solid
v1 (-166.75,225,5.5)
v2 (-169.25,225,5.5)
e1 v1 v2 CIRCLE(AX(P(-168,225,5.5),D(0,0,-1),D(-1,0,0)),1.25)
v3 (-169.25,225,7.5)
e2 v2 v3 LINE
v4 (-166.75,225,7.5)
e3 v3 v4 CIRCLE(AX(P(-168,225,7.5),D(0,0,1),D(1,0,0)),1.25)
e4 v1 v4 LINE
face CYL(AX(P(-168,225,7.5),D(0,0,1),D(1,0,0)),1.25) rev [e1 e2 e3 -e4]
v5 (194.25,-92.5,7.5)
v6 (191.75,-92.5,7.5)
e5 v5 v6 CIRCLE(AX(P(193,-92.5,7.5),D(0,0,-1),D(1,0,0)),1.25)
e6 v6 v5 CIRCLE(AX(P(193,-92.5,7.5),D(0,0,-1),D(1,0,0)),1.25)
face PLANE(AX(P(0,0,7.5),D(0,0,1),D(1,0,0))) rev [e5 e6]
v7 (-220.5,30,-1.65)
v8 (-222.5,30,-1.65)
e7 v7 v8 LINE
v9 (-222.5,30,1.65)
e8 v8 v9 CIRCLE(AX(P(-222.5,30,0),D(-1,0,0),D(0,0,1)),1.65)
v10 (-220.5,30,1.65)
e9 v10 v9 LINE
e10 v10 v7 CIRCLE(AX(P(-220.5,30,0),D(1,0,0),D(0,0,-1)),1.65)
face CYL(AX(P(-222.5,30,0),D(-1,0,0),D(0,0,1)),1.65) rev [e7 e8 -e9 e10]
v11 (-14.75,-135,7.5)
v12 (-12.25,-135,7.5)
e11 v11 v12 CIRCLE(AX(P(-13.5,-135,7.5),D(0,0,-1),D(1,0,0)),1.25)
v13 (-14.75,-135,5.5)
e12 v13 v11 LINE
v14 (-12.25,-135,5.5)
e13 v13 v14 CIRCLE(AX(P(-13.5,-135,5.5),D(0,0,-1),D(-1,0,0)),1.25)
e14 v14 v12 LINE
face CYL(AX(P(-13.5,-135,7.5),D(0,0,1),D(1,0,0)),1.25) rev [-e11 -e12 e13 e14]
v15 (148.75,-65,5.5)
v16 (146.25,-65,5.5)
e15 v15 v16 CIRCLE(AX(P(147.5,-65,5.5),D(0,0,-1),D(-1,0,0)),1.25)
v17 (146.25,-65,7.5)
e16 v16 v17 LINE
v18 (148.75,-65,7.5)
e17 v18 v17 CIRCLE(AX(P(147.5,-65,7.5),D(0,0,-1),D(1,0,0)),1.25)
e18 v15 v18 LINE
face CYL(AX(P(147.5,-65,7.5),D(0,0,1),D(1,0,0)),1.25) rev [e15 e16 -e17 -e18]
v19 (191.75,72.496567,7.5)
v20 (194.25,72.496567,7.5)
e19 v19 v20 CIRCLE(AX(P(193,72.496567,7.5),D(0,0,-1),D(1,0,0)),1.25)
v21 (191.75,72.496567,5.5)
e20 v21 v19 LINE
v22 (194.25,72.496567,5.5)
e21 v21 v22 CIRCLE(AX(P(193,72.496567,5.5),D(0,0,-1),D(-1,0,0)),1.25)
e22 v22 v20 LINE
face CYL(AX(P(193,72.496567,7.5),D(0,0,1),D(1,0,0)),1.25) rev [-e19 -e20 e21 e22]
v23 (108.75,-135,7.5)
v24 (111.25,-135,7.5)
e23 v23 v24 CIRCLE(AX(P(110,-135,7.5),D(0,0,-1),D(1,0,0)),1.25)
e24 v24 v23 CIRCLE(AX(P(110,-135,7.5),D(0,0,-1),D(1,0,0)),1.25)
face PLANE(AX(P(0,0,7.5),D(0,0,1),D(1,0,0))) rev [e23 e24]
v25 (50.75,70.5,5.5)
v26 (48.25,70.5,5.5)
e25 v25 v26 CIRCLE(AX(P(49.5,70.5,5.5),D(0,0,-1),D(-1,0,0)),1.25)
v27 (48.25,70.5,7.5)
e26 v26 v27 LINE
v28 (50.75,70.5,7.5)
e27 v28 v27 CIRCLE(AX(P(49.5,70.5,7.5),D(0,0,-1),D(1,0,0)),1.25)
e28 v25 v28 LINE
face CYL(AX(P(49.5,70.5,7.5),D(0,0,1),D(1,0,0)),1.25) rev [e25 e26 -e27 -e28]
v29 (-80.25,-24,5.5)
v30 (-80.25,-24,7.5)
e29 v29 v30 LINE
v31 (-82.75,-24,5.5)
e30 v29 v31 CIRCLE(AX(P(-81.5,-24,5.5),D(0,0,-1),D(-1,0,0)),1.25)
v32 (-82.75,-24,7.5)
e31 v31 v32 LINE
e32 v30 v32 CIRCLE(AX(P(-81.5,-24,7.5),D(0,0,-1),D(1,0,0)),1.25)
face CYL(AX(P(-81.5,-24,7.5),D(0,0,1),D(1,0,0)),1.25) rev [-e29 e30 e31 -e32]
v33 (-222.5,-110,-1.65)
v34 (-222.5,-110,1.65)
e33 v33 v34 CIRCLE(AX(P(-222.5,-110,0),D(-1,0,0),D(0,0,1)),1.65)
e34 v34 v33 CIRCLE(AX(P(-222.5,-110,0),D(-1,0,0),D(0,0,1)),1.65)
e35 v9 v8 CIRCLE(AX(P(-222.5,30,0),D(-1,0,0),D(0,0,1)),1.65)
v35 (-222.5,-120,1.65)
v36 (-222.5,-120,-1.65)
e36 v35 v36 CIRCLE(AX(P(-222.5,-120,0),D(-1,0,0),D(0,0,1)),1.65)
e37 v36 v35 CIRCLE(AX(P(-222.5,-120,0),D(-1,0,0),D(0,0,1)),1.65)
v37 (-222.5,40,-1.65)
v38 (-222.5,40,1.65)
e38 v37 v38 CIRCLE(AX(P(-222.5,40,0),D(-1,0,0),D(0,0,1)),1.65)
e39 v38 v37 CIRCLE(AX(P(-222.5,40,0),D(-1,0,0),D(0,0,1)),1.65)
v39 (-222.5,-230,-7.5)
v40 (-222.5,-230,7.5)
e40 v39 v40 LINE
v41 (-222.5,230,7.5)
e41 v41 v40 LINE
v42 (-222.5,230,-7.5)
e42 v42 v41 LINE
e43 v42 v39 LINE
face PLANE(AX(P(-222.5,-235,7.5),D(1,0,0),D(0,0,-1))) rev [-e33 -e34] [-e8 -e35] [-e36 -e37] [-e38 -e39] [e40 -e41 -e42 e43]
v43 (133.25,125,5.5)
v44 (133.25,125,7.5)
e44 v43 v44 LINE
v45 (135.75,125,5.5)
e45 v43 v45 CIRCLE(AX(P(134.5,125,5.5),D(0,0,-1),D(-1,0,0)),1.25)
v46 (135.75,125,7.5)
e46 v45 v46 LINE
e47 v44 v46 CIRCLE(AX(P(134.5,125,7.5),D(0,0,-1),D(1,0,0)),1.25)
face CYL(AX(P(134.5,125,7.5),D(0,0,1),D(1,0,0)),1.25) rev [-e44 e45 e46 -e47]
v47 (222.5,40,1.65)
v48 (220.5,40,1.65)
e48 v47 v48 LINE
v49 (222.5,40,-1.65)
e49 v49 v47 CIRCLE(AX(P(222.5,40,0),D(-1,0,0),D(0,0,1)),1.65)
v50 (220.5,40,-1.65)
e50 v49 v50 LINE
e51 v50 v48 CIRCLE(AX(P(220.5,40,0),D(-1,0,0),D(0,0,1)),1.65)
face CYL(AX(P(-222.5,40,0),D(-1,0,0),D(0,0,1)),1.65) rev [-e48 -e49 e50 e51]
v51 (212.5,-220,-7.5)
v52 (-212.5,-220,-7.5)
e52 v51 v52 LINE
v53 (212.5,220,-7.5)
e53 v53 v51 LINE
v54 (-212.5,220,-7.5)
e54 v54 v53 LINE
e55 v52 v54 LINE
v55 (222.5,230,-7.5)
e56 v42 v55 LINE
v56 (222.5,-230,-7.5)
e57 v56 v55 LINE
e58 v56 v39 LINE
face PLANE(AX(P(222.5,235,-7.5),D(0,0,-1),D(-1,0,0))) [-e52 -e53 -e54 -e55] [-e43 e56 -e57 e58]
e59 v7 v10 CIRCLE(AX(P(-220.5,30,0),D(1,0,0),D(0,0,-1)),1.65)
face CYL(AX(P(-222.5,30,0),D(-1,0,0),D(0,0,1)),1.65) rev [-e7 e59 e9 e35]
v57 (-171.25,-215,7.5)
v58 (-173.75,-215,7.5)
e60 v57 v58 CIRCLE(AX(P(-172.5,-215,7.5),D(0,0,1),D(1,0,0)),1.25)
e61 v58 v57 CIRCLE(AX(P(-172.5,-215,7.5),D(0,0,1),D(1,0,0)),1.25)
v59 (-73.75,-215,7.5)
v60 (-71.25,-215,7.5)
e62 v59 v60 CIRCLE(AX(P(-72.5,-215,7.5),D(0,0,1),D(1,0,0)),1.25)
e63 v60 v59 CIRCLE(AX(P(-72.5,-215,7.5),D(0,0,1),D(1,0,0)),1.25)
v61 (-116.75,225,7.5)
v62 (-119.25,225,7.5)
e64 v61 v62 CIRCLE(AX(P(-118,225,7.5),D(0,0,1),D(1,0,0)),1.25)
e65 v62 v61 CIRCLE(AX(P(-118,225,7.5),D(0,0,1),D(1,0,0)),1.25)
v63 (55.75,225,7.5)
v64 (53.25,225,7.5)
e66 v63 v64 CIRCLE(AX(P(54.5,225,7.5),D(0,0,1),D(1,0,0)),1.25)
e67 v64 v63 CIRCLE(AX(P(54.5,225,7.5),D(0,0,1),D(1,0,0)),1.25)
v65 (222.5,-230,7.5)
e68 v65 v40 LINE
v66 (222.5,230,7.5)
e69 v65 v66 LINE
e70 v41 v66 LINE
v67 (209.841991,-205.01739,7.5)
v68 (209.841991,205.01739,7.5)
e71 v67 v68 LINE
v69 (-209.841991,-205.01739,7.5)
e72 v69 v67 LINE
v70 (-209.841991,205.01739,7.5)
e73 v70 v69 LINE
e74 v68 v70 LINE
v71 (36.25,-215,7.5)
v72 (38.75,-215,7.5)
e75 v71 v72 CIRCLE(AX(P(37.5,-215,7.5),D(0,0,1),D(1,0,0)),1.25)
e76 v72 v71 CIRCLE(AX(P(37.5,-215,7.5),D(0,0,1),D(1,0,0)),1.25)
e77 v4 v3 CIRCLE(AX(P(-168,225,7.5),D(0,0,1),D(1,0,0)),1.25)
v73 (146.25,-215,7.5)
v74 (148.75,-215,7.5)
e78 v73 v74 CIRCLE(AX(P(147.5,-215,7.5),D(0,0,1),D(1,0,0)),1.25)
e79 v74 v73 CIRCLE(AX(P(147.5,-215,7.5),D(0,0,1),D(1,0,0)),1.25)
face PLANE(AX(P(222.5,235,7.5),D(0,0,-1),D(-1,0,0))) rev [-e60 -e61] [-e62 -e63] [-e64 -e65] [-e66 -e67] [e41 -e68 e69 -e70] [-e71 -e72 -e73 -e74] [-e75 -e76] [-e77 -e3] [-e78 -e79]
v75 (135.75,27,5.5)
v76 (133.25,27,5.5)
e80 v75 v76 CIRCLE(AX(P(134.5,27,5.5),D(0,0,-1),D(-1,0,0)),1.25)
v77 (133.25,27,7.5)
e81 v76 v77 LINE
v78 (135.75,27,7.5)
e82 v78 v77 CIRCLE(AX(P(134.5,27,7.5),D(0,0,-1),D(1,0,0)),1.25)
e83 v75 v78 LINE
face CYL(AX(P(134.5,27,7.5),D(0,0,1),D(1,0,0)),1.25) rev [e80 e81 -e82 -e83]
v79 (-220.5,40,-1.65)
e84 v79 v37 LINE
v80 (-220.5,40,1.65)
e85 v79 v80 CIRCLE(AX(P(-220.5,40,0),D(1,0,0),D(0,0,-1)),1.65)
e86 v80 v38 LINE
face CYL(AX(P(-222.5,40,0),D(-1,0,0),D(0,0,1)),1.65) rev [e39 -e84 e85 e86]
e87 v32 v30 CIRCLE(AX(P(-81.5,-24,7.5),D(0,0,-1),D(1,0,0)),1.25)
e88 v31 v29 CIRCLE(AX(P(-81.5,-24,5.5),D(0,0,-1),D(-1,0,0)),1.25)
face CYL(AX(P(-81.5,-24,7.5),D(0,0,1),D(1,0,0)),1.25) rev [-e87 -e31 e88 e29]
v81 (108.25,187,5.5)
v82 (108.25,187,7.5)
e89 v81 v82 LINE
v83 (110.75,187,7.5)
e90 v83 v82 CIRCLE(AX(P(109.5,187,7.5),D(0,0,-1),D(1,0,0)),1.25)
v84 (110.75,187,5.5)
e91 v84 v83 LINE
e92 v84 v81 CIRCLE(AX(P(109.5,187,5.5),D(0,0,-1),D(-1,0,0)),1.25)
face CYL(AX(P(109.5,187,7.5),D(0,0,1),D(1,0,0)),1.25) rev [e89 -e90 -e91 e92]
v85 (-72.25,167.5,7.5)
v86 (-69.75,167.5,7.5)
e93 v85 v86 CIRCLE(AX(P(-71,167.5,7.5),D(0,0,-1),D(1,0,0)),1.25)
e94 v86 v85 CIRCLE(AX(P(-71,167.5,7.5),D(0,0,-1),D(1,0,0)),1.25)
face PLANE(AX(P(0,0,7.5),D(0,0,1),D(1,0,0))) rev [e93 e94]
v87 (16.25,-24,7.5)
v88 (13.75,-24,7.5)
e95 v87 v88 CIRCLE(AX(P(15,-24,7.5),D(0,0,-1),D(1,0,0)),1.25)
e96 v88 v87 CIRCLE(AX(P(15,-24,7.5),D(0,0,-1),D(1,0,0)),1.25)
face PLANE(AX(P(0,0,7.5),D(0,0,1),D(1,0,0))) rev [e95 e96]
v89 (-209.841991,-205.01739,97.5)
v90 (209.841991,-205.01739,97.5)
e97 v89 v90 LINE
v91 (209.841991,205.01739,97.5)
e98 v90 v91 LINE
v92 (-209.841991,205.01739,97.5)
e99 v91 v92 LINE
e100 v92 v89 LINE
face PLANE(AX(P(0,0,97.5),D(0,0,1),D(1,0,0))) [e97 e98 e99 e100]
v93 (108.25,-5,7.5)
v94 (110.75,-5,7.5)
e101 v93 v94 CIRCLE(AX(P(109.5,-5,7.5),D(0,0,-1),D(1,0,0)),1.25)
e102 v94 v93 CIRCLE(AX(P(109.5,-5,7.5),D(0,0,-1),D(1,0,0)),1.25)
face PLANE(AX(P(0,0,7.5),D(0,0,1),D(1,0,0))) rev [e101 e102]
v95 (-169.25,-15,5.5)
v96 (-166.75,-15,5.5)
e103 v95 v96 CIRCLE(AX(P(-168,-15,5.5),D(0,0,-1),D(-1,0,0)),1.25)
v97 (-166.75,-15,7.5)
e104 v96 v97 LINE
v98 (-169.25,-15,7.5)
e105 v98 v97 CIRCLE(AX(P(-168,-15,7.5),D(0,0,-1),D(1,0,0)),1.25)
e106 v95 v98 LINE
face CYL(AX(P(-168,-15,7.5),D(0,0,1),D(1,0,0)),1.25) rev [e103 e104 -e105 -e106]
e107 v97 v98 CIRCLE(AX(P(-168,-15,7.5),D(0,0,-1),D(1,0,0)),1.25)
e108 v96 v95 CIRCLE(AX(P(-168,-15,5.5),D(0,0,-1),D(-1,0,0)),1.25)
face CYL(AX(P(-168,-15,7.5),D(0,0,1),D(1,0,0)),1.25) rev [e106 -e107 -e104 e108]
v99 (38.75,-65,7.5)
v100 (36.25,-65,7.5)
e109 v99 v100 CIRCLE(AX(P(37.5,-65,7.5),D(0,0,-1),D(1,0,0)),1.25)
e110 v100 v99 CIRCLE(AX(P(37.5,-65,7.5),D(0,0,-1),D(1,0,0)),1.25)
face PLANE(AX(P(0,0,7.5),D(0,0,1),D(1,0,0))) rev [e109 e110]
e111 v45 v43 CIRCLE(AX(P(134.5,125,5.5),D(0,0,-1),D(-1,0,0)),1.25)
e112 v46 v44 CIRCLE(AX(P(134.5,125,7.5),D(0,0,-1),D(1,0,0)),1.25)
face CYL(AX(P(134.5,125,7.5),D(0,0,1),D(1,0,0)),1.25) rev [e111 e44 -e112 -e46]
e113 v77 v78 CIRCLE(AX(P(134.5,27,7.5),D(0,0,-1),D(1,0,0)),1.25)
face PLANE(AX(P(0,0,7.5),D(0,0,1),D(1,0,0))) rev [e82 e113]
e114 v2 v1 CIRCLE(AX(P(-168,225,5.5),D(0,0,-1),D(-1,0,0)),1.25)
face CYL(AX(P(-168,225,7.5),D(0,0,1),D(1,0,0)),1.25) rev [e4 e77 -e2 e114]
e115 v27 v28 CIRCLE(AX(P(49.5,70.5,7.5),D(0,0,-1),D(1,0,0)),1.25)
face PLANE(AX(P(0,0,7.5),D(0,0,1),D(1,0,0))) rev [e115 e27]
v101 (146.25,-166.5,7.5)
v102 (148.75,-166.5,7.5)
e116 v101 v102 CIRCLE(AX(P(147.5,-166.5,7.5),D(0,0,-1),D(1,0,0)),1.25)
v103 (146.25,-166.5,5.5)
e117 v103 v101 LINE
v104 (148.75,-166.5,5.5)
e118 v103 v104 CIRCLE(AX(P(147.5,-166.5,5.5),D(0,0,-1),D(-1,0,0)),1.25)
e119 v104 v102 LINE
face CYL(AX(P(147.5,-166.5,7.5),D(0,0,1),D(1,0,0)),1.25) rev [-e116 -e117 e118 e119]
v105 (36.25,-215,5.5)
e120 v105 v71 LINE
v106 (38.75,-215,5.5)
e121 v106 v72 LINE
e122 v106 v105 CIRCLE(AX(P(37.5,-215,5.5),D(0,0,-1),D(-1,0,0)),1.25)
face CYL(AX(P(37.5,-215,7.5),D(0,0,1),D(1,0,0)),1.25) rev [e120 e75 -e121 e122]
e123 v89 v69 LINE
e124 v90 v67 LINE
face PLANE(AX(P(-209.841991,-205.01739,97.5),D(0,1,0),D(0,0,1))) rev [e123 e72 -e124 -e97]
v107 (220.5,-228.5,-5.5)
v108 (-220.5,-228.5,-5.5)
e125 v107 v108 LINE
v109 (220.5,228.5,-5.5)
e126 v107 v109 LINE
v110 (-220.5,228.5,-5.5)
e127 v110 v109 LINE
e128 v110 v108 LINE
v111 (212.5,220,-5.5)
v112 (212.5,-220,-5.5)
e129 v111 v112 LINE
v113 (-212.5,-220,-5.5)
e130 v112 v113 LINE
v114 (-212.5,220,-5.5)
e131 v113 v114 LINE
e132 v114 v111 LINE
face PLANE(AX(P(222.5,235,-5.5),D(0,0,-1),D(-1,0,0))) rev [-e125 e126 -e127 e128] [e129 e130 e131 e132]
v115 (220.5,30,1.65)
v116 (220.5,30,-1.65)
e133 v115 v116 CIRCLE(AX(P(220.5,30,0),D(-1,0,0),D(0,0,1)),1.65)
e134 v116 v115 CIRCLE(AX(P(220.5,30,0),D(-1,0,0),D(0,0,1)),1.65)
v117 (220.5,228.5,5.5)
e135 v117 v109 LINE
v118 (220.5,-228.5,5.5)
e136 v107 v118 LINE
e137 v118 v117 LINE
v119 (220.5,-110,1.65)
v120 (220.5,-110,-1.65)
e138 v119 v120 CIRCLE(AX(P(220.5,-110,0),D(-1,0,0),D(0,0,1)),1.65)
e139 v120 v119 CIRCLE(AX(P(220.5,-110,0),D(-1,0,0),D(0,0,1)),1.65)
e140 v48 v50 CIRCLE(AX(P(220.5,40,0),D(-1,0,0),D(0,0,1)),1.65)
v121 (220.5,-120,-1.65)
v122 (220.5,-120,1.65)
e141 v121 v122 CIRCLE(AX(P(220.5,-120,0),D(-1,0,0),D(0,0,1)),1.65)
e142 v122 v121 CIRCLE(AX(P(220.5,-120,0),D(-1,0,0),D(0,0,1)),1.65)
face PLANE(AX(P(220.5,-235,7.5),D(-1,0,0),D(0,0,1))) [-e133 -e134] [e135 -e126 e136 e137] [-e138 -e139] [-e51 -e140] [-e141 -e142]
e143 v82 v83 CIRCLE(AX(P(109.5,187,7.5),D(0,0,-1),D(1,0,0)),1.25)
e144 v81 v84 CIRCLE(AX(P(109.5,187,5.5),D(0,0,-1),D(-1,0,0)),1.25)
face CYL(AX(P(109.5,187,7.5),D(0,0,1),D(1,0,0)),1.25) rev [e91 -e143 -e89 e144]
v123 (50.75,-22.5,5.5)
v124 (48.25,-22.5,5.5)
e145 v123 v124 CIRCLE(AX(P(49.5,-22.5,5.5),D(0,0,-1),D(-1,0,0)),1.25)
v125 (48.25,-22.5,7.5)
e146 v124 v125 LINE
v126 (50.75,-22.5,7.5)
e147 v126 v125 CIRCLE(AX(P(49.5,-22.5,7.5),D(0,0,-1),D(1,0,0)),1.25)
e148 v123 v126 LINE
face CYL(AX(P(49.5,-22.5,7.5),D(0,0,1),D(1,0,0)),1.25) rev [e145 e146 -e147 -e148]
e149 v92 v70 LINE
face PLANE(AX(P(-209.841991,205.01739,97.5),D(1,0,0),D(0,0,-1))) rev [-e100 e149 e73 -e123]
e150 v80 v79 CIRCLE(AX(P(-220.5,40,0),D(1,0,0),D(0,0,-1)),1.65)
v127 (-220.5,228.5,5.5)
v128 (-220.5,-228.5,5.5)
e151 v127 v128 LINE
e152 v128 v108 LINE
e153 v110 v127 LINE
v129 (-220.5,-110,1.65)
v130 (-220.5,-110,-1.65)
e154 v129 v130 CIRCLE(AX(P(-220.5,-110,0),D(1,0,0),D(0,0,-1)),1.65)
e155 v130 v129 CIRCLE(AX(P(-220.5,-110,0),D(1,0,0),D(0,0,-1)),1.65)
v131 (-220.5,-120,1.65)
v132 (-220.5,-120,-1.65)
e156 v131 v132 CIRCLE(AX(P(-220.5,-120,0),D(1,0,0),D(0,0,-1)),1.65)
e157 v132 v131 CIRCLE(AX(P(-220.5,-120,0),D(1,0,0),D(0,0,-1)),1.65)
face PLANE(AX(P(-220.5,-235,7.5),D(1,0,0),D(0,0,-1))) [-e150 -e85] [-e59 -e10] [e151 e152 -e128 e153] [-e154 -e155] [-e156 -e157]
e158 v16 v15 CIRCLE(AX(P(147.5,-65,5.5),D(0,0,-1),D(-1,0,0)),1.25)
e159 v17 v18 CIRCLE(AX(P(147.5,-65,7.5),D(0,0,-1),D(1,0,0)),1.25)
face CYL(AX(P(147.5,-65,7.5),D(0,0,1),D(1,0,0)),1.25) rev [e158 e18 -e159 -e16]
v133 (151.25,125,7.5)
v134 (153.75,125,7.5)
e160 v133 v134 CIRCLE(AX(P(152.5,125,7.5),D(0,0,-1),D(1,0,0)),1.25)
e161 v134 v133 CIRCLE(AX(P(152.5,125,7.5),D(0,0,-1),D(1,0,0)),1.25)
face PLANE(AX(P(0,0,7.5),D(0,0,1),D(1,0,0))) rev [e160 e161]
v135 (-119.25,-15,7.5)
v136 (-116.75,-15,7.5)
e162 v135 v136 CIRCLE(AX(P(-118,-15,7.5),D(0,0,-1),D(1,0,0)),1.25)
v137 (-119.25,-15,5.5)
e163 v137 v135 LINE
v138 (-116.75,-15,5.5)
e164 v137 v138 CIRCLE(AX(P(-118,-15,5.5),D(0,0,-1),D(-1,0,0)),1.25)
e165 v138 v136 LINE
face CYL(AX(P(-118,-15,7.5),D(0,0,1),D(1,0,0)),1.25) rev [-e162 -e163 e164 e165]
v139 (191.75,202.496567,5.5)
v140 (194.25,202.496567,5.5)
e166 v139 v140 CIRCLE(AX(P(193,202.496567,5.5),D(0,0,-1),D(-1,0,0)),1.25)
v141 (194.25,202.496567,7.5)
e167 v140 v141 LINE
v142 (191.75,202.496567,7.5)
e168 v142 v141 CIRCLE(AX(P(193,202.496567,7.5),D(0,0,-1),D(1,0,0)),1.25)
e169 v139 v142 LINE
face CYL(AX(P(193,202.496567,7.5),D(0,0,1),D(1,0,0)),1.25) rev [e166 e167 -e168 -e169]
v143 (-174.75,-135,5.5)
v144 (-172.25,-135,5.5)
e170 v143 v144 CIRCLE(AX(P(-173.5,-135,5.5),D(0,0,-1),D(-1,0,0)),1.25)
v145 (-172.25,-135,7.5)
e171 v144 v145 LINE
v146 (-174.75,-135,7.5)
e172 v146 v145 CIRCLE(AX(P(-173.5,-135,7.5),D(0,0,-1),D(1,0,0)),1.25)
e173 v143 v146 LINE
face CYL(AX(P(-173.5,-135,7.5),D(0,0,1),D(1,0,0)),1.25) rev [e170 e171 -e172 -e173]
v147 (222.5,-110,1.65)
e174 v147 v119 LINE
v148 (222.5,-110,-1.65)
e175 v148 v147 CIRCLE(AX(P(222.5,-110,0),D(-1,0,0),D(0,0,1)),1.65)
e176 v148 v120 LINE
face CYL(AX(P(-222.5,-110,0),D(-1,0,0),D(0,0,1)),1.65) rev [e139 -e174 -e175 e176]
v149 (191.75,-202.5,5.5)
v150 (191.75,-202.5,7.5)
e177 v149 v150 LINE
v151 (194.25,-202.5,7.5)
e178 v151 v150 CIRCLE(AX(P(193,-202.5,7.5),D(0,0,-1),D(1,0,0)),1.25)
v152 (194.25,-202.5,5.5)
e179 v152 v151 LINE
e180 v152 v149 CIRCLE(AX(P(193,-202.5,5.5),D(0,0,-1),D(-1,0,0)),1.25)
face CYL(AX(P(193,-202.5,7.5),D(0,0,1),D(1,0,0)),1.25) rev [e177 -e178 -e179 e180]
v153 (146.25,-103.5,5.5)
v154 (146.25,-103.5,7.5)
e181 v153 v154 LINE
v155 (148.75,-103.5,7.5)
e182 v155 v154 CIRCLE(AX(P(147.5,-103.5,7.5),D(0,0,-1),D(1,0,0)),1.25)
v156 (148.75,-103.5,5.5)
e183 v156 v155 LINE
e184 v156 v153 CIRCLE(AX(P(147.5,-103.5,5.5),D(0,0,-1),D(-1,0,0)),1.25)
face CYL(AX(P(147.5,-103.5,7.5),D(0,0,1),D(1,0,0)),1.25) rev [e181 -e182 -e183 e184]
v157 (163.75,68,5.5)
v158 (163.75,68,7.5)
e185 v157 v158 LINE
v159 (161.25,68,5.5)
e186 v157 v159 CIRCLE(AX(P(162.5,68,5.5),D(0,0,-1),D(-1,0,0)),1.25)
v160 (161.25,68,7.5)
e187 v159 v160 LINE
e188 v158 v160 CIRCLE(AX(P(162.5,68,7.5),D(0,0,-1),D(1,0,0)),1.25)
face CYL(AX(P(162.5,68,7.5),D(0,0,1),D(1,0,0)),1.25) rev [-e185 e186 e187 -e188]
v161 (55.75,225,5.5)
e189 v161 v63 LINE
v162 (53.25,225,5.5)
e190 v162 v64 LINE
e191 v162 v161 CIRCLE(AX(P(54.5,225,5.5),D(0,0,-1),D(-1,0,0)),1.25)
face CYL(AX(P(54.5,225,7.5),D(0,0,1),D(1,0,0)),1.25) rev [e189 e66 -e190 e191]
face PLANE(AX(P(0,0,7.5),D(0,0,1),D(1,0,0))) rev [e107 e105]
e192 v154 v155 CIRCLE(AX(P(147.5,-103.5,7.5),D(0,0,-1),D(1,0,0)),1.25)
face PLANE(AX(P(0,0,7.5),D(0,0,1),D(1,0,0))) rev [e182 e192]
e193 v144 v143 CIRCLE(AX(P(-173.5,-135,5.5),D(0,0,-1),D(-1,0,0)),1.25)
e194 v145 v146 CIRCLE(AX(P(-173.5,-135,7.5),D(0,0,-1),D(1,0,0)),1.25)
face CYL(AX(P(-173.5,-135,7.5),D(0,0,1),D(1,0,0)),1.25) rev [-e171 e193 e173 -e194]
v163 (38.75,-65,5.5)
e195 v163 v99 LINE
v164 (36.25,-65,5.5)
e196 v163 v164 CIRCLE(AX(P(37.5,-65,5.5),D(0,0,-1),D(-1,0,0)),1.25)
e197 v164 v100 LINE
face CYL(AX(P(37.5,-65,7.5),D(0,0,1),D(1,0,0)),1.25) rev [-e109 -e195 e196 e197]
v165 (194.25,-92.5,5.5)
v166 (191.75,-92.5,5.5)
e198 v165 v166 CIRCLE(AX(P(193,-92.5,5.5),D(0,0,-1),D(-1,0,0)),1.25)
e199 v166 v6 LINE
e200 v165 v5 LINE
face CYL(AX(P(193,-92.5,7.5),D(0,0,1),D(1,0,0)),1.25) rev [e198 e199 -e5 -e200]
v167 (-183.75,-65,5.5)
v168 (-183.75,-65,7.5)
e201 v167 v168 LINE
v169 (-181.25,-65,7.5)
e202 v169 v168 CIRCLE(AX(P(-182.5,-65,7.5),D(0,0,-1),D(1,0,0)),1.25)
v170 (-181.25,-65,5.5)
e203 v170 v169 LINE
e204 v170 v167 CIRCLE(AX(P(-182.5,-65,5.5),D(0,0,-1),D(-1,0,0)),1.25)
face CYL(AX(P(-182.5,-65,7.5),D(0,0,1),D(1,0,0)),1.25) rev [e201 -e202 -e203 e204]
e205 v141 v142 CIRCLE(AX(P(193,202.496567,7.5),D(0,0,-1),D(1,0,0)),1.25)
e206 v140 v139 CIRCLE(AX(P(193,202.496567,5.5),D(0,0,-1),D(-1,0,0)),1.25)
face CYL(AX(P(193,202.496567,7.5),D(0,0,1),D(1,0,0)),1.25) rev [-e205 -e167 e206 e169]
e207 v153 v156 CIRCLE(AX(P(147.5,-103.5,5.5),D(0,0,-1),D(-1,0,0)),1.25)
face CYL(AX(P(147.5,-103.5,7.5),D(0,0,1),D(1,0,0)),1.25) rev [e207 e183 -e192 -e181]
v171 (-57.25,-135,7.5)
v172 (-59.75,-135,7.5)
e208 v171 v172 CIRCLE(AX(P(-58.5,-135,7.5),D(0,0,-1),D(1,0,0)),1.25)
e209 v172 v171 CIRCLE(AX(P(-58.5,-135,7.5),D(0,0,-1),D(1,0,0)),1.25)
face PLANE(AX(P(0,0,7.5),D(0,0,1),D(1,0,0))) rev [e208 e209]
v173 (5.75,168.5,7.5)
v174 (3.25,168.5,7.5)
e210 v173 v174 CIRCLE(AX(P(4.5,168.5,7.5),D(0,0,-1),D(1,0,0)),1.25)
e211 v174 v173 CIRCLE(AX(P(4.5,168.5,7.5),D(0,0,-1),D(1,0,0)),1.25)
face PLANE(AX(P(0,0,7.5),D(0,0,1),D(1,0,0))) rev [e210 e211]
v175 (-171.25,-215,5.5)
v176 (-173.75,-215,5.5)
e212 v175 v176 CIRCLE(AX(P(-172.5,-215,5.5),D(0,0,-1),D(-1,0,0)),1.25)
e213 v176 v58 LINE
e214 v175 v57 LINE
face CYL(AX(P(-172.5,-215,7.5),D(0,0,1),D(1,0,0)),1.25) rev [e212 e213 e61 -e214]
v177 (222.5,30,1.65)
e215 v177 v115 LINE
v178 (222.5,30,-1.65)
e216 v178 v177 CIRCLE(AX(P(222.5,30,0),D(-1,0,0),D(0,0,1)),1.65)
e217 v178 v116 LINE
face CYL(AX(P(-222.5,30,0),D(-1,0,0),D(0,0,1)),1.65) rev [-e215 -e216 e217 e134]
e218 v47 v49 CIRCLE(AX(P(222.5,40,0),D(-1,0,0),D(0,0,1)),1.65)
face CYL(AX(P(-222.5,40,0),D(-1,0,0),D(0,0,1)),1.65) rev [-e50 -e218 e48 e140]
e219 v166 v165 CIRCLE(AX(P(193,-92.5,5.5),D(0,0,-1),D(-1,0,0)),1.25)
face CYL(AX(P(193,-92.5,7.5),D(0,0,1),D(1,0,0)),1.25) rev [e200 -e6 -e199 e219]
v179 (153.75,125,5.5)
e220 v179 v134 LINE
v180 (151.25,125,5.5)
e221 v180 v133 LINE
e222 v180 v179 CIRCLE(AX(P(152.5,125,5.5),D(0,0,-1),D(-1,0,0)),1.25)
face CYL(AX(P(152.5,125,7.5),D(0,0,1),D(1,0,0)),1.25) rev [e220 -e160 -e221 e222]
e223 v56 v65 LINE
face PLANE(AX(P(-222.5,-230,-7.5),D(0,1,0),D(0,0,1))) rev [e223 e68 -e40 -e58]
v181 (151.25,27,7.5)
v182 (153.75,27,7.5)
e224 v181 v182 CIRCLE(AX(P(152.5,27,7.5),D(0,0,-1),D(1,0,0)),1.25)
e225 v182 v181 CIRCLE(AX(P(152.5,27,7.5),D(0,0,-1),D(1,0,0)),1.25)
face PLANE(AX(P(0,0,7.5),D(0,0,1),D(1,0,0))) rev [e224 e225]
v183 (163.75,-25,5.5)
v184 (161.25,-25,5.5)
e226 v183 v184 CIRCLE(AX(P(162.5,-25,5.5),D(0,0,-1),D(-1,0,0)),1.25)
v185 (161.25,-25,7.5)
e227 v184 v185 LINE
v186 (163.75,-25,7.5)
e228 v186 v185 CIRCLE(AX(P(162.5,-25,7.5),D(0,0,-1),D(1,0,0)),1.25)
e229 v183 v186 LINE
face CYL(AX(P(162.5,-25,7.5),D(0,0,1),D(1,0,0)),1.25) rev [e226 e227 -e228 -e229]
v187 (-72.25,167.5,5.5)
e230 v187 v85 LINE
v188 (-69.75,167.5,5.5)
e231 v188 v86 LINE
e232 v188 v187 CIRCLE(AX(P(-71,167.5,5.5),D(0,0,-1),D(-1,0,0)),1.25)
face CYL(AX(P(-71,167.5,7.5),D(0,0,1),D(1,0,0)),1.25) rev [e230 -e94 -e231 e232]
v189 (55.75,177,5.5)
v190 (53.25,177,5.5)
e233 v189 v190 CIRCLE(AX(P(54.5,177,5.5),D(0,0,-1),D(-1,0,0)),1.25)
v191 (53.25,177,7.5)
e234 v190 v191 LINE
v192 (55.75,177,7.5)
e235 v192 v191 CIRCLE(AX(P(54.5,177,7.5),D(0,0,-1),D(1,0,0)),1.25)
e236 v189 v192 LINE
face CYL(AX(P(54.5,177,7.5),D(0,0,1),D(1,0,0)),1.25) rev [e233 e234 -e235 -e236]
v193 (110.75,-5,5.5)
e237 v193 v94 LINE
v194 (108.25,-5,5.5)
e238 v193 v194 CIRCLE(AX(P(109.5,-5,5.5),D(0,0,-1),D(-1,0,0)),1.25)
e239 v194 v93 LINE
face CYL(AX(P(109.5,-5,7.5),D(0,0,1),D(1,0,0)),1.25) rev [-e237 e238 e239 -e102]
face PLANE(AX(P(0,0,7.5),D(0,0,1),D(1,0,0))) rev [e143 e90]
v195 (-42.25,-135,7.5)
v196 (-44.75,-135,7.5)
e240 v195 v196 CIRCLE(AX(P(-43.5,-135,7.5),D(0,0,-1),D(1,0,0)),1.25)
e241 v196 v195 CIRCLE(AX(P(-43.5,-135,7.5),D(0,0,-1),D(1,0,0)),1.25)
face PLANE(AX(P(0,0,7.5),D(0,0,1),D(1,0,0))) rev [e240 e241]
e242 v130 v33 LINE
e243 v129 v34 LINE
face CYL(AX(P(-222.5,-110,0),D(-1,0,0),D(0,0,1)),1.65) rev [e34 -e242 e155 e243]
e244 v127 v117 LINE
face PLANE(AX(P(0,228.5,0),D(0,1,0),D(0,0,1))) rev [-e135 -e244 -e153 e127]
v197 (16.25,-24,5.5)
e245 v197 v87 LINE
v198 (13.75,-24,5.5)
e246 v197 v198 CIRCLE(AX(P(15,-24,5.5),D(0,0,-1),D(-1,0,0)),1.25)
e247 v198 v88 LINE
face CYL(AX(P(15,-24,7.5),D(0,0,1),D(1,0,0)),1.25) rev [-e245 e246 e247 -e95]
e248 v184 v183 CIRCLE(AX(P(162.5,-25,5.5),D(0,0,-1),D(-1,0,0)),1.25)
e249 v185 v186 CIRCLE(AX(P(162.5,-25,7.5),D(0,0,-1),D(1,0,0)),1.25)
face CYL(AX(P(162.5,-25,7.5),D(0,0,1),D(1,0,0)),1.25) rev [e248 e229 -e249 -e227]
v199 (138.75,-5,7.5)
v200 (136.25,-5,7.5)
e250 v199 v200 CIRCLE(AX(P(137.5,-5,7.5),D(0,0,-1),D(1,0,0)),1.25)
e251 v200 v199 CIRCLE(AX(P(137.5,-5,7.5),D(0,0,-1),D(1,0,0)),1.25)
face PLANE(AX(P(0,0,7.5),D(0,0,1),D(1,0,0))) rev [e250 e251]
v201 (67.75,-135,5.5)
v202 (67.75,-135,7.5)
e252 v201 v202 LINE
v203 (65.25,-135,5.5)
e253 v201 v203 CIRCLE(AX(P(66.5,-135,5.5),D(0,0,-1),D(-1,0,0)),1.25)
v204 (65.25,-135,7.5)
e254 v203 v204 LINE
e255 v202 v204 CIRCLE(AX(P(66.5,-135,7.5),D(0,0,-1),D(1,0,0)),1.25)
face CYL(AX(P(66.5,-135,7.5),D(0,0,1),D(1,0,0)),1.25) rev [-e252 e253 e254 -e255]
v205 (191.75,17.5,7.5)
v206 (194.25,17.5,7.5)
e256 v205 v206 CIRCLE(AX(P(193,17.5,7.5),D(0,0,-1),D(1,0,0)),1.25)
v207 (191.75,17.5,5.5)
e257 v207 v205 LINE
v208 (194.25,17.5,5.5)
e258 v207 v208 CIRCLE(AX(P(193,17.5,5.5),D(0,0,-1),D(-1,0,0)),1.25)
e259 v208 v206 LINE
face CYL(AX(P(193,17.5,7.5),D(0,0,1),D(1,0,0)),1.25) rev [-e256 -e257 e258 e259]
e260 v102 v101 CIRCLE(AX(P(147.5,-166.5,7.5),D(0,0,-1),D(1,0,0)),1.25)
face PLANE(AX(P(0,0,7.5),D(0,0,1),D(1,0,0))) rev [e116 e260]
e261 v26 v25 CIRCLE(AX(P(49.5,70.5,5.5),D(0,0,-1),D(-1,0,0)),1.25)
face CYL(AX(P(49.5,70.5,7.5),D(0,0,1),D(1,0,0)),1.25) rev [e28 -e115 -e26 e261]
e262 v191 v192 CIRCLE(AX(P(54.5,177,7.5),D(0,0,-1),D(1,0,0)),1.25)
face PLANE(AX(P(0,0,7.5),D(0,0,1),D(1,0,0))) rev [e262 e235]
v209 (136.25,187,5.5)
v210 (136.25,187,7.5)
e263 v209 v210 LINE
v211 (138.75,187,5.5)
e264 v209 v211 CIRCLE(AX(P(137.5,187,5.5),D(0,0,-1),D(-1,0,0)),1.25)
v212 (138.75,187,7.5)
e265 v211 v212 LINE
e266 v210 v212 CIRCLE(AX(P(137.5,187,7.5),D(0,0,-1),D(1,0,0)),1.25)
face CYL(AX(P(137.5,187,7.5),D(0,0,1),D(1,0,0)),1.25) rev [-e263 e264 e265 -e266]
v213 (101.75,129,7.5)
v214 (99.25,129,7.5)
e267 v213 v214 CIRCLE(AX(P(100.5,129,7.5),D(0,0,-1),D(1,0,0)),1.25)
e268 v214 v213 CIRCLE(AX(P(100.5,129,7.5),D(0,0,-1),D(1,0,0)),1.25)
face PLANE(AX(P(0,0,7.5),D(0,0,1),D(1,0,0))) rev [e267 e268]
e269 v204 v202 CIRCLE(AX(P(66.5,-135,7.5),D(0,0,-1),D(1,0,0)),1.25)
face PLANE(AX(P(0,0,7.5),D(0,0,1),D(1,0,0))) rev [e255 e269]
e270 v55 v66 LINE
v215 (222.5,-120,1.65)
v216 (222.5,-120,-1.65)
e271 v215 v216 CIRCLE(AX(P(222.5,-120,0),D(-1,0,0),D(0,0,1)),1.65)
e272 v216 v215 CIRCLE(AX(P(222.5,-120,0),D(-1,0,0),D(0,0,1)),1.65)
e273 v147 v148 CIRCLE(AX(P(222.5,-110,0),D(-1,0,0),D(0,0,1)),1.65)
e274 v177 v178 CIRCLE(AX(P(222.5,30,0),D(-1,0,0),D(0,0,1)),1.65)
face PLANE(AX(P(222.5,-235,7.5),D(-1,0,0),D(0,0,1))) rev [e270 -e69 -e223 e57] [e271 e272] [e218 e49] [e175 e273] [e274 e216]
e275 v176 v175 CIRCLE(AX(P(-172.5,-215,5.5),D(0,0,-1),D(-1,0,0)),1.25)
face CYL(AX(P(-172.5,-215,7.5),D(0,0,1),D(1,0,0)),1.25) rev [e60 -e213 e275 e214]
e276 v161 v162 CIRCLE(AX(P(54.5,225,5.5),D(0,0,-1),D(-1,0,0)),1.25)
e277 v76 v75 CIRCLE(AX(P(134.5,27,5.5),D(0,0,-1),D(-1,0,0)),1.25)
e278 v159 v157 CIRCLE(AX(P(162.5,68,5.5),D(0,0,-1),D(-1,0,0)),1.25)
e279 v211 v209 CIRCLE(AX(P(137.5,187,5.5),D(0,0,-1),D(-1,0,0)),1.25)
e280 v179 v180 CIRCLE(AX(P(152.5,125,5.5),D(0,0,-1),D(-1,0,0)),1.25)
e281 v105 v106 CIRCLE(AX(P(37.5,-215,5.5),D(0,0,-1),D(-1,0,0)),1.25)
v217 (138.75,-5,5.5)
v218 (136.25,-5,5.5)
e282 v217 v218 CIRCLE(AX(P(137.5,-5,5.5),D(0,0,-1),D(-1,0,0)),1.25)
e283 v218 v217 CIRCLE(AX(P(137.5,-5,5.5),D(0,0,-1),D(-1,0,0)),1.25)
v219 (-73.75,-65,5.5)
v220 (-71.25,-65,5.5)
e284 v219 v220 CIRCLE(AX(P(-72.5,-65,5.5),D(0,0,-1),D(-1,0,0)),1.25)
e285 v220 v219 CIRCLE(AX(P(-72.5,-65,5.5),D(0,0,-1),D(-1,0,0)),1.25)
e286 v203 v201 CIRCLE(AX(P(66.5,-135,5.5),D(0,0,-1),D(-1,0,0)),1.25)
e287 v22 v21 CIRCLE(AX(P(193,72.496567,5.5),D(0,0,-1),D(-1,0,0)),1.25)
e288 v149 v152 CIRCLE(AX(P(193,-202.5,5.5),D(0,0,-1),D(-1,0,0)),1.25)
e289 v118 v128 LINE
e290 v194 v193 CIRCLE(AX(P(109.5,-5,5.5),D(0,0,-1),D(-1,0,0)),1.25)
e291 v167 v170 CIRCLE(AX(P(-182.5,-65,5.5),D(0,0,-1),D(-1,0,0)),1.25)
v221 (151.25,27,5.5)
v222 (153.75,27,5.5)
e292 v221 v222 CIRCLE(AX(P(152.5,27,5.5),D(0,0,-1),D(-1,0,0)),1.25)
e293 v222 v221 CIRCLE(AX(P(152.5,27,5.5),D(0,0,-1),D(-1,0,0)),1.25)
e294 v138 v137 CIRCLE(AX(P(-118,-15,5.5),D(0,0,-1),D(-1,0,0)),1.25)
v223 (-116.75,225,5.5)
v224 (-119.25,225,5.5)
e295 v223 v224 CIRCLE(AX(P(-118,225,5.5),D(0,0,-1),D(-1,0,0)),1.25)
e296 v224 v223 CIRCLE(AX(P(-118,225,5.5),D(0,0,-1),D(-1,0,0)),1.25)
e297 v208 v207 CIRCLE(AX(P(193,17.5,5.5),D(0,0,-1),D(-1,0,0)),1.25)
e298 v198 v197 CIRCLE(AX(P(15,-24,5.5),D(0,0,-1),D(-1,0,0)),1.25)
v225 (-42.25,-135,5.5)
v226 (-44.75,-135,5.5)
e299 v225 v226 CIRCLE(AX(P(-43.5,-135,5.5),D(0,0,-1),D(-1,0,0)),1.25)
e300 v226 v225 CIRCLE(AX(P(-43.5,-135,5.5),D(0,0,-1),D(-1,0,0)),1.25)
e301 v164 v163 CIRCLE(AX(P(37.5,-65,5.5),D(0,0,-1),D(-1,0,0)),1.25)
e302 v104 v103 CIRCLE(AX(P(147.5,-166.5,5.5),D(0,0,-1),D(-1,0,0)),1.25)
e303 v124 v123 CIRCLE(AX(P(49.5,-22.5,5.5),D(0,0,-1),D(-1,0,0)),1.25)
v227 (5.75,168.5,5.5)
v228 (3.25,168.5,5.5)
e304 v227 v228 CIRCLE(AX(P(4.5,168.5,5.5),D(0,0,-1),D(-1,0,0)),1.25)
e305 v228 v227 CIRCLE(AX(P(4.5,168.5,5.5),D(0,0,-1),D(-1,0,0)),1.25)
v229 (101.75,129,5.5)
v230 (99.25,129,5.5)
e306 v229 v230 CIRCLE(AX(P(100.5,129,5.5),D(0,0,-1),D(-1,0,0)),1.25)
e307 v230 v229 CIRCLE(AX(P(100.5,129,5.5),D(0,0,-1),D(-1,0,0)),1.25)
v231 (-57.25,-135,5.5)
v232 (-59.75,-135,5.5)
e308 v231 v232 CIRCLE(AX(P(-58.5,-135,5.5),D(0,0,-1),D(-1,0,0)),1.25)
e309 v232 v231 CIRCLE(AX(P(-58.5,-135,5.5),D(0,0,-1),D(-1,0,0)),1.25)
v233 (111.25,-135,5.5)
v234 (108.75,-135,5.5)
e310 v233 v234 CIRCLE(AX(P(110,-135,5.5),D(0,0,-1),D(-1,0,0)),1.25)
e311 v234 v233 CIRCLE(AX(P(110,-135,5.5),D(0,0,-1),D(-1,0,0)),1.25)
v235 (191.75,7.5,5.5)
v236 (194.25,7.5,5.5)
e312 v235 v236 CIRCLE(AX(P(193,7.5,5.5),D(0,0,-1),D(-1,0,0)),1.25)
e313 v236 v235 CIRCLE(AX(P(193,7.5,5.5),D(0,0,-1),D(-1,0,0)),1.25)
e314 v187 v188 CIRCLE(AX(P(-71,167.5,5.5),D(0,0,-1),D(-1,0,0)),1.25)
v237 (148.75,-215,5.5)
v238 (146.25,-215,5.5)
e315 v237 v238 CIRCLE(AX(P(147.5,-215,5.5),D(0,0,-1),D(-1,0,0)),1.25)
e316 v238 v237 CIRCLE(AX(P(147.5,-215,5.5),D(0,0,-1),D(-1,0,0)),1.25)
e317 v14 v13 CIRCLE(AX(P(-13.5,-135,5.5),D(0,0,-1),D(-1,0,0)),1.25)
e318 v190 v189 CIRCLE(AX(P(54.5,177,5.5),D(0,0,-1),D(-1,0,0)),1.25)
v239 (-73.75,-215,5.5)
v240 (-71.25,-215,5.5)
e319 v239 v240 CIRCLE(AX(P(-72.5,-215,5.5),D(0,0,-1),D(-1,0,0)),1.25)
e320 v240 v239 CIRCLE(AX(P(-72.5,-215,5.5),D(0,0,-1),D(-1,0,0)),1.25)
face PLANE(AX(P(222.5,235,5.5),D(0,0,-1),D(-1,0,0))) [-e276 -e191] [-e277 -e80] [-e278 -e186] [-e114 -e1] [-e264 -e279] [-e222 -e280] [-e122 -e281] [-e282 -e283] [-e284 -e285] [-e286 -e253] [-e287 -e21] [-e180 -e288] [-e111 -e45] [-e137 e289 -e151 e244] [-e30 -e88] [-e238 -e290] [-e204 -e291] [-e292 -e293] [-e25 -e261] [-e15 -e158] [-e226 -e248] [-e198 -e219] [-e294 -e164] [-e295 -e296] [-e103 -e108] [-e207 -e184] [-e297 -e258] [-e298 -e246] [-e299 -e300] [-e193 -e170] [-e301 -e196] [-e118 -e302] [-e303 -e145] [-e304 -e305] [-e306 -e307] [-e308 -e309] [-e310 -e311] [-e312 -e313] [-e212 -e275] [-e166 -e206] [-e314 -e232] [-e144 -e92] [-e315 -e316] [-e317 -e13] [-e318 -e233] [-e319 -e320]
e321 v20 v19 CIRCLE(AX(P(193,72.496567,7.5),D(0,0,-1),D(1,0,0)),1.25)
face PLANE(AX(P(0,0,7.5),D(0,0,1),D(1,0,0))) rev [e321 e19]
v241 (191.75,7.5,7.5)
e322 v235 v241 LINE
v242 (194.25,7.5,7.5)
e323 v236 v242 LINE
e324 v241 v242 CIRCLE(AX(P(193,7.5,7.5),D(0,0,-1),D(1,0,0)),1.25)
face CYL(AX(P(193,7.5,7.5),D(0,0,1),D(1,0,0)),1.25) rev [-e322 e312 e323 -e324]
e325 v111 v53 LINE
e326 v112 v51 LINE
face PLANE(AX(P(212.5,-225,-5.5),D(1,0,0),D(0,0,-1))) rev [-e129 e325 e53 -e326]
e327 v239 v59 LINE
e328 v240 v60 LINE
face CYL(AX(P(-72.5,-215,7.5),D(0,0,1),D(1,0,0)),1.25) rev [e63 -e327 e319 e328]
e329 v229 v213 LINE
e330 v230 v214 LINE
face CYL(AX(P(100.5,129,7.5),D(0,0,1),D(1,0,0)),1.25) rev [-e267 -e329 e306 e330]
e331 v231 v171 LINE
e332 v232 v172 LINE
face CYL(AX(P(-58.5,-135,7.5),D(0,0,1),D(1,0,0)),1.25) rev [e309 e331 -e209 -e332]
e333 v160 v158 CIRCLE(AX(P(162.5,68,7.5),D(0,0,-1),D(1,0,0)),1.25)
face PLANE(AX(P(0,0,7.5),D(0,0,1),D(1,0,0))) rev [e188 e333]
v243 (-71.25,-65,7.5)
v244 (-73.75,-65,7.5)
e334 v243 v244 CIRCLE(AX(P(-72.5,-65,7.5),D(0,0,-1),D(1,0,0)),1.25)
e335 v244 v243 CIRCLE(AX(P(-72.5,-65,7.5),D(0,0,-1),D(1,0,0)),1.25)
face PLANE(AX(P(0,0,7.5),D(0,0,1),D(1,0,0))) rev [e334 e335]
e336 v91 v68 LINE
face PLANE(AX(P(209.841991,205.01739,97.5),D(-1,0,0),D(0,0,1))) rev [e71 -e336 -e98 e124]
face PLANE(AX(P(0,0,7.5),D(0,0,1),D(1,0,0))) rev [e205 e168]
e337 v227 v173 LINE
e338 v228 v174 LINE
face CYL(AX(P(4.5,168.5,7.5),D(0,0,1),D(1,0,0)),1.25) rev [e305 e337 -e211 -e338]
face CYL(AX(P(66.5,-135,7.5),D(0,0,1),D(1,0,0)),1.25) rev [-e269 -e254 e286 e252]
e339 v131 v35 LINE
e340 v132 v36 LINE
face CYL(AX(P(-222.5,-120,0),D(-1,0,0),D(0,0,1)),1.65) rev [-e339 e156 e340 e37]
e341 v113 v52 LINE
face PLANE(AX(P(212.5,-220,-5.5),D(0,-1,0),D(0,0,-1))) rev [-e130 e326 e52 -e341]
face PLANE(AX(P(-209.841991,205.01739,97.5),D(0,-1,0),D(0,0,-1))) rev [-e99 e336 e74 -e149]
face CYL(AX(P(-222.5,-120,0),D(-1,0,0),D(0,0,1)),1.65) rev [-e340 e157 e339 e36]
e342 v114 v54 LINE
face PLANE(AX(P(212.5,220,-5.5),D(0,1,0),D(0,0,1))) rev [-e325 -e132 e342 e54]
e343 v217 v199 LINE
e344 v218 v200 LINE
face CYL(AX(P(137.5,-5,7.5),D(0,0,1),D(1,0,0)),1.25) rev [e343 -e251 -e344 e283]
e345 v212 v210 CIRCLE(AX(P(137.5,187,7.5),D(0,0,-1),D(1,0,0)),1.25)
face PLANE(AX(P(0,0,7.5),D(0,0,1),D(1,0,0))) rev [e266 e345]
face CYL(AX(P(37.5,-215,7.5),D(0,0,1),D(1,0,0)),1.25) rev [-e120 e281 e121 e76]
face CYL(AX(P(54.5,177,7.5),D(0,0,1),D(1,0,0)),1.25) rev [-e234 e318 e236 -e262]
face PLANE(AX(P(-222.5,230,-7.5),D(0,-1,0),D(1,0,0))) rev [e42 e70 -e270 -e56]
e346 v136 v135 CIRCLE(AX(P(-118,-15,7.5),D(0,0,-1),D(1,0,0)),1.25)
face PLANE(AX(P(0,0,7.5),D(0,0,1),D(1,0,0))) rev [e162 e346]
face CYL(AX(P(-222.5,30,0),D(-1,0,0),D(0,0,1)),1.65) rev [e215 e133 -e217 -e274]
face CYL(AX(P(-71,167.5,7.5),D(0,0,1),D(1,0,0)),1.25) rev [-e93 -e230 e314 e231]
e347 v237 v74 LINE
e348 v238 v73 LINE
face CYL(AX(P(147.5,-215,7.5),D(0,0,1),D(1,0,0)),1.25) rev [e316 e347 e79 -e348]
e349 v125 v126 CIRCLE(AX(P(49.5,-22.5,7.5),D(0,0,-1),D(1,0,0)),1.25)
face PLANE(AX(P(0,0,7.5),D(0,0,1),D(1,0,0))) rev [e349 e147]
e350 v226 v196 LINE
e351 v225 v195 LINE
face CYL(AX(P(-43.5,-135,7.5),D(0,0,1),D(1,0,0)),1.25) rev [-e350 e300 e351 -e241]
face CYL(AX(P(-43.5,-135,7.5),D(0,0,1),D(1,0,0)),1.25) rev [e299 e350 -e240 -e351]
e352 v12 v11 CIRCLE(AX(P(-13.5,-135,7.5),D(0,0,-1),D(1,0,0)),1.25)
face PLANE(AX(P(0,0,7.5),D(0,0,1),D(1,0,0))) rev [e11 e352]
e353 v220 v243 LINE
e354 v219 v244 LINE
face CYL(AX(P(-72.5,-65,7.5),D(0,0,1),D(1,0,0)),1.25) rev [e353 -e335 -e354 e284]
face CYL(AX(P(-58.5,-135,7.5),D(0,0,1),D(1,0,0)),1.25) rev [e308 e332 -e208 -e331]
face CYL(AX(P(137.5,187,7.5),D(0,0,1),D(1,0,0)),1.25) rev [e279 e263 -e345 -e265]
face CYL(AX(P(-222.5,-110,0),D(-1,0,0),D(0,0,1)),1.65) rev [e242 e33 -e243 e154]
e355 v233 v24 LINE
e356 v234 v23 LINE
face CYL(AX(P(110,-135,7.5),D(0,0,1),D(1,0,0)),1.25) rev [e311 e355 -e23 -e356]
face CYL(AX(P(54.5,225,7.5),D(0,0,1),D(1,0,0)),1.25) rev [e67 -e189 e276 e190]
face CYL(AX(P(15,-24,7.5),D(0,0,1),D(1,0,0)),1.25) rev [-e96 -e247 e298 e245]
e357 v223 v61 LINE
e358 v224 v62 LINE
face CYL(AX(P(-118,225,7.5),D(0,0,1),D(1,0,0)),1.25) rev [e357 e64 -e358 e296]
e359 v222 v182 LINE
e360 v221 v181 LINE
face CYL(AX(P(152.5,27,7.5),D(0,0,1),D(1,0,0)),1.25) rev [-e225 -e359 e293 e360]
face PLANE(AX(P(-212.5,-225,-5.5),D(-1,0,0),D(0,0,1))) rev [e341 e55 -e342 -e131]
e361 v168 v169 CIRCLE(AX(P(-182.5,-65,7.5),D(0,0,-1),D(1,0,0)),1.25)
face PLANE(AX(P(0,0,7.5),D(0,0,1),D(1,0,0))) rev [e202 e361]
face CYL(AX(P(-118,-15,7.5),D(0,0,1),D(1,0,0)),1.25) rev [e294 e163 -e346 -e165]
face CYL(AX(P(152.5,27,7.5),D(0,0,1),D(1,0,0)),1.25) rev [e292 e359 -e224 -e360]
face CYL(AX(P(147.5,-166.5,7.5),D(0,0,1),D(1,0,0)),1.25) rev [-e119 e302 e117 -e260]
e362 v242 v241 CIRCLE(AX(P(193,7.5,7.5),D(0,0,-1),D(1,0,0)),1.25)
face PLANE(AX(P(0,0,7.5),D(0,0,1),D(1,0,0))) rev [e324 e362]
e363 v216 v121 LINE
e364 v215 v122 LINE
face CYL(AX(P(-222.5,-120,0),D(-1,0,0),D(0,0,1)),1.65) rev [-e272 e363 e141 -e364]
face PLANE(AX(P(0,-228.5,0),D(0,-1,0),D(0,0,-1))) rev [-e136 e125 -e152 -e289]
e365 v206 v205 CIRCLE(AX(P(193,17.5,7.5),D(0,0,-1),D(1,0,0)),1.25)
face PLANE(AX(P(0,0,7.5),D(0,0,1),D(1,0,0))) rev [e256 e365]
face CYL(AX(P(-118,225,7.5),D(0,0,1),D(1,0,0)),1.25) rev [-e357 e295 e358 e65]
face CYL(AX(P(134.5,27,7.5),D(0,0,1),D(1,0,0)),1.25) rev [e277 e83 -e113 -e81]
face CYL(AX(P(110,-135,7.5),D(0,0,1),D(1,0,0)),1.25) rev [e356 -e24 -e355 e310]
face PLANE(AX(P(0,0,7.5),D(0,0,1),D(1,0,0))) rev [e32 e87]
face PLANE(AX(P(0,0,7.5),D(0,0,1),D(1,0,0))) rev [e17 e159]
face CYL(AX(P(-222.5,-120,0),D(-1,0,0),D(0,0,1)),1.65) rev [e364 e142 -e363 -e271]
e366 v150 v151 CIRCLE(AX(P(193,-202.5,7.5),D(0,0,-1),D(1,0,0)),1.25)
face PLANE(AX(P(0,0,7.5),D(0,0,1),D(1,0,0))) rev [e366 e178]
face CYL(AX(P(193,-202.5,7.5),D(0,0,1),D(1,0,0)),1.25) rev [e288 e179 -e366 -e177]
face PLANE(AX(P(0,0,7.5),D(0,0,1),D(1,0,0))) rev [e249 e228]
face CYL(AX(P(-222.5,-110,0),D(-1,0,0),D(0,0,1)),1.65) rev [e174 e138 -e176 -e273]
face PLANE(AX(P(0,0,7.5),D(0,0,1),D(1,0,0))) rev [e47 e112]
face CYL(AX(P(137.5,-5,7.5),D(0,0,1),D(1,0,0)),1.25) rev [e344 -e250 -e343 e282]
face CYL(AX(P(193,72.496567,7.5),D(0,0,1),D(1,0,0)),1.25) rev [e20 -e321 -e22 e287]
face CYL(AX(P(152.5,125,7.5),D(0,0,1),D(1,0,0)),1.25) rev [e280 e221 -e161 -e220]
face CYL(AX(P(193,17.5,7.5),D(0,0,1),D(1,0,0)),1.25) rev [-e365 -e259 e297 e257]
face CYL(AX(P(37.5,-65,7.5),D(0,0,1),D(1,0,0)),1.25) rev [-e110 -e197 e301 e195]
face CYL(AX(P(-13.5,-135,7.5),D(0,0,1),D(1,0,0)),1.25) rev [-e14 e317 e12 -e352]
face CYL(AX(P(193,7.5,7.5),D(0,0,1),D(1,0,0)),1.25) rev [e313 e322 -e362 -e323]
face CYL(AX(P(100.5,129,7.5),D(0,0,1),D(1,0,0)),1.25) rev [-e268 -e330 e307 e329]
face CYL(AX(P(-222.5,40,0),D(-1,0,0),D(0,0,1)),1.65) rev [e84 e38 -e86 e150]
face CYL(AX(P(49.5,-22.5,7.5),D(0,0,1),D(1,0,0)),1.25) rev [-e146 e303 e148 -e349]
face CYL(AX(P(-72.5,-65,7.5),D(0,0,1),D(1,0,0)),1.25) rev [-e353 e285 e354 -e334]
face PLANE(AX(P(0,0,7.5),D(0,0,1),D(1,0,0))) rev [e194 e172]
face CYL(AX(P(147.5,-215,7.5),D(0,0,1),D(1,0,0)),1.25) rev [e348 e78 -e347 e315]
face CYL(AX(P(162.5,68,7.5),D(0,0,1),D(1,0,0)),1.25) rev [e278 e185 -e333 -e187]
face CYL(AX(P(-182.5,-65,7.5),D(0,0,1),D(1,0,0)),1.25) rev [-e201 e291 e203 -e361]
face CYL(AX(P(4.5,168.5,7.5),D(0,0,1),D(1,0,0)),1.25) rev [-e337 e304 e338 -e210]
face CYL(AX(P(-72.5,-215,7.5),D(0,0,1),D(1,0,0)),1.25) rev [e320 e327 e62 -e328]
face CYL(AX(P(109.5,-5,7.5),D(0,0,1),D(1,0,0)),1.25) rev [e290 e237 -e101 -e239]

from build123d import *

# Parameters (mm, degrees)
SKETCH_1_W             = 445
SKETCH_1_H             = 470
EXTRUDE_1_DEPTH        = 7.5
SHELL_1_T              = 2
SKETCH_2_W             = 425
SKETCH_2_H             = 450
CUT_EXTRUDE_1_DEPTH    = 2
CUT_EXTRUDE_2_DEPTH    = 10
HOLE_WIZARD_M3_1_D     = 2.5
HOLE_WIZARD_M3_1_DEPTH = 7.5
SKETCH_9_W             = 445
SKETCH_9_H             = 5
CUT_EXTRUDE_4_DEPTH    = 324.969520171
SKETCH_10_W            = 445
SKETCH_10_H            = 15
EXTRUDE_2_DEPTH        = 1.5
SKETCH_11_W            = 445
SKETCH_11_H            = 15
EXTRUDE_3_DEPTH        = 1.5
MOVE_FACE_1_BY         = 5
MOVE_FACE_2_BY         = 5
EXTRUDE_4_DEPTH        = 2
HOLE_WIZARD_M4_1_D     = 3.3
HOLE_WIZARD_M3_2_D     = 2.5
HOLE_WIZARD_M3_3_D     = 2.5
PATTERN_LINEAR_1_COUNT = 2
PATTERN_LINEAR_1_PITCH = 10
HOLE_WIZARD_M3_4_D     = 2.5
SKETCH_26_W            = 419.683981368
SKETCH_26_H            = 410.034779602
EXTRUDE_5_DEPTH        = 90


with BuildPart() as part:
    # 草图1 → 凸台-拉伸1 (new, symmetric)
    with BuildSketch(Plane.XY):
        Rectangle(SKETCH_1_W, SKETCH_1_H)
    extrude(amount=EXTRUDE_1_DEPTH, both=True)

    # 抽壳1 (no face opened: a closed hollow body)
    add(offset(amount=-SHELL_1_T, mode=Mode.PRIVATE), mode=Mode.SUBTRACT)

    # 草图2 → 切除-拉伸1 (cut)
    with BuildSketch(Plane(origin=(0, 0, -7.5), x_dir=(-1, 0, 0), z_dir=(0, 0, -1))):
        Rectangle(SKETCH_2_W, SKETCH_2_H)
    extrude(amount=-CUT_EXTRUDE_1_DEPTH, mode=Mode.SUBTRACT)

    # 草图3 → 切除-拉伸2 (cut)
    with BuildSketch(Plane.XY.offset(7.5)):
        with BuildLine():
            Line((-205, 152.5), (-195, 152.5))
            ThreePointArc((-195, 152.5), (-192.5, 150), (-195, 147.5))
            Line((-195, 147.5), (-205, 147.5))
            ThreePointArc((-205, 147.5), (-207.5, 150), (-205, 152.5))
        make_face()
        with BuildLine():
            Line((195, 152.5), (205, 152.5))
            ThreePointArc((205, 152.5), (207.5, 150), (205, 147.5))
            Line((205, 147.5), (195, 147.5))
            ThreePointArc((195, 147.5), (192.5, 150), (195, 152.5))
        make_face()
        with BuildLine():
            Line((-205, -147.5), (-195, -147.5))
            ThreePointArc((-195, -147.5), (-192.5, -150), (-195, -152.5))
            Line((-195, -152.5), (-205, -152.5))
            ThreePointArc((-205, -152.5), (-207.5, -150), (-205, -147.5))
        make_face()
        with BuildLine():
            Line((195, -147.5), (205, -147.5))
            ThreePointArc((205, -147.5), (207.5, -150), (205, -152.5))
            Line((205, -152.5), (195, -152.5))
            ThreePointArc((195, -152.5), (192.5, -150), (195, -147.5))
        make_face()
    extrude(amount=-CUT_EXTRUDE_2_DEPTH, mode=Mode.SUBTRACT)

    # M3 螺纹孔1
    with Locations(Plane.XY.offset(7.5)):
        with Locations((-72.5, -215), (-172.5, -215), (37.5, -215), (147.5, -215), (193, -202.5), (147.5, -166.5), (66.5, -135), (-13.5, -135), (-58.5, -135), (-173.5, -135), (-182.5, -65), (-168, -15), (-118, -15), (-72.5, -65), (-81.5, -24), (37.5, -65), (15, -24), (49.5, -22.5), (147.5, -103.5), (193, -92.5), (147.5, -65), (162.5, -25), (193, 7.5), (193, 17.5), (193, 72.496566859), (162.5, 68), (152.5, 27), (134.5, 27), (100.5, 129), (49.5, 70.5), (193, 202.496566859), (152.5, 125), (134.5, 125), (54.5, 177), (54.5, 225), (4.5, 168.5), (-118, 225), (-168, 225)):
            Hole(HOLE_WIZARD_M3_1_D / 2, depth=HOLE_WIZARD_M3_1_DEPTH)

    # 草图9 → 切除-拉伸4 (cut, through all)
    with BuildSketch(Plane.XY.offset(7.5)):
        with Locations((0, 232.5)):
            Rectangle(SKETCH_9_W, SKETCH_9_H)
        with Locations((0, -232.5)):
            Rectangle(SKETCH_9_W, SKETCH_9_H)
    extrude(amount=-CUT_EXTRUDE_4_DEPTH, mode=Mode.SUBTRACT)

    # 草图10 → 凸台-拉伸2 (add)
    with BuildSketch(Plane(origin=(0, 230, 0), x_dir=(1, 0, 0), z_dir=(0, 1, 0))):
        Rectangle(SKETCH_10_W, SKETCH_10_H)
    extrude(amount=-EXTRUDE_2_DEPTH)

    # 草图11 → 凸台-拉伸3 (add)
    with BuildSketch(Plane.XZ.offset(230)):
        Rectangle(SKETCH_11_W, SKETCH_11_H)
    extrude(amount=-EXTRUDE_3_DEPTH)

    # Move Face 1: a face moved outward by 5.0
    extrude(part.faces().sort_by_distance((0, 225, -6.5))[0], amount=MOVE_FACE_1_BY, dir=(0, -1, 0))

    # Move Face 2: a face moved outward by 5.0
    extrude(part.faces().sort_by_distance((0, -225, -6.5))[0], amount=MOVE_FACE_2_BY, dir=(0, 1, 0))

    # 草图12 → 凸台-拉伸4 (add)
    with BuildSketch(Plane.XY.offset(7.5)):
        with BuildLine():
            Line((-195, 152.5), (-205, 152.5))
            ThreePointArc((-205, 152.5), (-207.5, 150), (-205, 147.5))
            Line((-205, 147.5), (-195, 147.5))
            ThreePointArc((-195, 147.5), (-192.5, 150), (-195, 152.5))
        make_face()
        with BuildLine():
            Line((-195, -147.5), (-205, -147.5))
            ThreePointArc((-205, -147.5), (-207.5, -150), (-205, -152.5))
            Line((-205, -152.5), (-195, -152.5))
            ThreePointArc((-195, -152.5), (-192.5, -150), (-195, -147.5))
        make_face()
        with BuildLine():
            Line((205, 152.5), (195, 152.5))
            ThreePointArc((195, 152.5), (192.5, 150), (195, 147.5))
            Line((195, 147.5), (205, 147.5))
            ThreePointArc((205, 147.5), (207.5, 150), (205, 152.5))
        make_face()
        with BuildLine():
            Line((205, -147.5), (195, -147.5))
            ThreePointArc((195, -147.5), (192.5, -150), (195, -152.5))
            Line((195, -152.5), (205, -152.5))
            ThreePointArc((205, -152.5), (207.5, -150), (205, -147.5))
        make_face()
    extrude(amount=-EXTRUDE_4_DEPTH)

    # M4 螺纹孔1 (through all)
    with Locations(Plane.ZY.offset(222.5)):
        with Locations((0, 30), (0, -120)):
            hole_wizard_m4_1 = Hole(HOLE_WIZARD_M4_1_D / 2)

    # M3 螺纹孔2 (through all)
    with Locations(Plane.XY.offset(7.5)):
        with Locations((-43.5, -135), (110, -135)):
            Hole(HOLE_WIZARD_M3_2_D / 2)

    # M3 螺纹孔3 (through all)
    with Locations(Plane.XY.offset(7.5)):
        with Locations((-71, 167.5)):
            Hole(HOLE_WIZARD_M3_3_D / 2)

    # 阵列(线性)1: M4 螺纹孔1 ×2
    with Locations(*[(0, i * PATTERN_LINEAR_1_PITCH, 0) for i in range(1, PATTERN_LINEAR_1_COUNT)]):
        add(hole_wizard_m4_1, mode=Mode.SUBTRACT)

    # M3 螺纹孔4 (through all)
    with Locations(Plane.XY.offset(7.5)):
        with Locations((109.5, 187), (137.5, 187), (109.5, -5), (137.5, -5)):
            Hole(HOLE_WIZARD_M3_4_D / 2)

    # 草图26 → 凸台-拉伸5 (add)
    with BuildSketch(Plane.XY.offset(7.5)):
        Rectangle(SKETCH_26_W, SKETCH_26_H)
    extrude(amount=EXTRUDE_5_DEPTH)


solid = part.part
